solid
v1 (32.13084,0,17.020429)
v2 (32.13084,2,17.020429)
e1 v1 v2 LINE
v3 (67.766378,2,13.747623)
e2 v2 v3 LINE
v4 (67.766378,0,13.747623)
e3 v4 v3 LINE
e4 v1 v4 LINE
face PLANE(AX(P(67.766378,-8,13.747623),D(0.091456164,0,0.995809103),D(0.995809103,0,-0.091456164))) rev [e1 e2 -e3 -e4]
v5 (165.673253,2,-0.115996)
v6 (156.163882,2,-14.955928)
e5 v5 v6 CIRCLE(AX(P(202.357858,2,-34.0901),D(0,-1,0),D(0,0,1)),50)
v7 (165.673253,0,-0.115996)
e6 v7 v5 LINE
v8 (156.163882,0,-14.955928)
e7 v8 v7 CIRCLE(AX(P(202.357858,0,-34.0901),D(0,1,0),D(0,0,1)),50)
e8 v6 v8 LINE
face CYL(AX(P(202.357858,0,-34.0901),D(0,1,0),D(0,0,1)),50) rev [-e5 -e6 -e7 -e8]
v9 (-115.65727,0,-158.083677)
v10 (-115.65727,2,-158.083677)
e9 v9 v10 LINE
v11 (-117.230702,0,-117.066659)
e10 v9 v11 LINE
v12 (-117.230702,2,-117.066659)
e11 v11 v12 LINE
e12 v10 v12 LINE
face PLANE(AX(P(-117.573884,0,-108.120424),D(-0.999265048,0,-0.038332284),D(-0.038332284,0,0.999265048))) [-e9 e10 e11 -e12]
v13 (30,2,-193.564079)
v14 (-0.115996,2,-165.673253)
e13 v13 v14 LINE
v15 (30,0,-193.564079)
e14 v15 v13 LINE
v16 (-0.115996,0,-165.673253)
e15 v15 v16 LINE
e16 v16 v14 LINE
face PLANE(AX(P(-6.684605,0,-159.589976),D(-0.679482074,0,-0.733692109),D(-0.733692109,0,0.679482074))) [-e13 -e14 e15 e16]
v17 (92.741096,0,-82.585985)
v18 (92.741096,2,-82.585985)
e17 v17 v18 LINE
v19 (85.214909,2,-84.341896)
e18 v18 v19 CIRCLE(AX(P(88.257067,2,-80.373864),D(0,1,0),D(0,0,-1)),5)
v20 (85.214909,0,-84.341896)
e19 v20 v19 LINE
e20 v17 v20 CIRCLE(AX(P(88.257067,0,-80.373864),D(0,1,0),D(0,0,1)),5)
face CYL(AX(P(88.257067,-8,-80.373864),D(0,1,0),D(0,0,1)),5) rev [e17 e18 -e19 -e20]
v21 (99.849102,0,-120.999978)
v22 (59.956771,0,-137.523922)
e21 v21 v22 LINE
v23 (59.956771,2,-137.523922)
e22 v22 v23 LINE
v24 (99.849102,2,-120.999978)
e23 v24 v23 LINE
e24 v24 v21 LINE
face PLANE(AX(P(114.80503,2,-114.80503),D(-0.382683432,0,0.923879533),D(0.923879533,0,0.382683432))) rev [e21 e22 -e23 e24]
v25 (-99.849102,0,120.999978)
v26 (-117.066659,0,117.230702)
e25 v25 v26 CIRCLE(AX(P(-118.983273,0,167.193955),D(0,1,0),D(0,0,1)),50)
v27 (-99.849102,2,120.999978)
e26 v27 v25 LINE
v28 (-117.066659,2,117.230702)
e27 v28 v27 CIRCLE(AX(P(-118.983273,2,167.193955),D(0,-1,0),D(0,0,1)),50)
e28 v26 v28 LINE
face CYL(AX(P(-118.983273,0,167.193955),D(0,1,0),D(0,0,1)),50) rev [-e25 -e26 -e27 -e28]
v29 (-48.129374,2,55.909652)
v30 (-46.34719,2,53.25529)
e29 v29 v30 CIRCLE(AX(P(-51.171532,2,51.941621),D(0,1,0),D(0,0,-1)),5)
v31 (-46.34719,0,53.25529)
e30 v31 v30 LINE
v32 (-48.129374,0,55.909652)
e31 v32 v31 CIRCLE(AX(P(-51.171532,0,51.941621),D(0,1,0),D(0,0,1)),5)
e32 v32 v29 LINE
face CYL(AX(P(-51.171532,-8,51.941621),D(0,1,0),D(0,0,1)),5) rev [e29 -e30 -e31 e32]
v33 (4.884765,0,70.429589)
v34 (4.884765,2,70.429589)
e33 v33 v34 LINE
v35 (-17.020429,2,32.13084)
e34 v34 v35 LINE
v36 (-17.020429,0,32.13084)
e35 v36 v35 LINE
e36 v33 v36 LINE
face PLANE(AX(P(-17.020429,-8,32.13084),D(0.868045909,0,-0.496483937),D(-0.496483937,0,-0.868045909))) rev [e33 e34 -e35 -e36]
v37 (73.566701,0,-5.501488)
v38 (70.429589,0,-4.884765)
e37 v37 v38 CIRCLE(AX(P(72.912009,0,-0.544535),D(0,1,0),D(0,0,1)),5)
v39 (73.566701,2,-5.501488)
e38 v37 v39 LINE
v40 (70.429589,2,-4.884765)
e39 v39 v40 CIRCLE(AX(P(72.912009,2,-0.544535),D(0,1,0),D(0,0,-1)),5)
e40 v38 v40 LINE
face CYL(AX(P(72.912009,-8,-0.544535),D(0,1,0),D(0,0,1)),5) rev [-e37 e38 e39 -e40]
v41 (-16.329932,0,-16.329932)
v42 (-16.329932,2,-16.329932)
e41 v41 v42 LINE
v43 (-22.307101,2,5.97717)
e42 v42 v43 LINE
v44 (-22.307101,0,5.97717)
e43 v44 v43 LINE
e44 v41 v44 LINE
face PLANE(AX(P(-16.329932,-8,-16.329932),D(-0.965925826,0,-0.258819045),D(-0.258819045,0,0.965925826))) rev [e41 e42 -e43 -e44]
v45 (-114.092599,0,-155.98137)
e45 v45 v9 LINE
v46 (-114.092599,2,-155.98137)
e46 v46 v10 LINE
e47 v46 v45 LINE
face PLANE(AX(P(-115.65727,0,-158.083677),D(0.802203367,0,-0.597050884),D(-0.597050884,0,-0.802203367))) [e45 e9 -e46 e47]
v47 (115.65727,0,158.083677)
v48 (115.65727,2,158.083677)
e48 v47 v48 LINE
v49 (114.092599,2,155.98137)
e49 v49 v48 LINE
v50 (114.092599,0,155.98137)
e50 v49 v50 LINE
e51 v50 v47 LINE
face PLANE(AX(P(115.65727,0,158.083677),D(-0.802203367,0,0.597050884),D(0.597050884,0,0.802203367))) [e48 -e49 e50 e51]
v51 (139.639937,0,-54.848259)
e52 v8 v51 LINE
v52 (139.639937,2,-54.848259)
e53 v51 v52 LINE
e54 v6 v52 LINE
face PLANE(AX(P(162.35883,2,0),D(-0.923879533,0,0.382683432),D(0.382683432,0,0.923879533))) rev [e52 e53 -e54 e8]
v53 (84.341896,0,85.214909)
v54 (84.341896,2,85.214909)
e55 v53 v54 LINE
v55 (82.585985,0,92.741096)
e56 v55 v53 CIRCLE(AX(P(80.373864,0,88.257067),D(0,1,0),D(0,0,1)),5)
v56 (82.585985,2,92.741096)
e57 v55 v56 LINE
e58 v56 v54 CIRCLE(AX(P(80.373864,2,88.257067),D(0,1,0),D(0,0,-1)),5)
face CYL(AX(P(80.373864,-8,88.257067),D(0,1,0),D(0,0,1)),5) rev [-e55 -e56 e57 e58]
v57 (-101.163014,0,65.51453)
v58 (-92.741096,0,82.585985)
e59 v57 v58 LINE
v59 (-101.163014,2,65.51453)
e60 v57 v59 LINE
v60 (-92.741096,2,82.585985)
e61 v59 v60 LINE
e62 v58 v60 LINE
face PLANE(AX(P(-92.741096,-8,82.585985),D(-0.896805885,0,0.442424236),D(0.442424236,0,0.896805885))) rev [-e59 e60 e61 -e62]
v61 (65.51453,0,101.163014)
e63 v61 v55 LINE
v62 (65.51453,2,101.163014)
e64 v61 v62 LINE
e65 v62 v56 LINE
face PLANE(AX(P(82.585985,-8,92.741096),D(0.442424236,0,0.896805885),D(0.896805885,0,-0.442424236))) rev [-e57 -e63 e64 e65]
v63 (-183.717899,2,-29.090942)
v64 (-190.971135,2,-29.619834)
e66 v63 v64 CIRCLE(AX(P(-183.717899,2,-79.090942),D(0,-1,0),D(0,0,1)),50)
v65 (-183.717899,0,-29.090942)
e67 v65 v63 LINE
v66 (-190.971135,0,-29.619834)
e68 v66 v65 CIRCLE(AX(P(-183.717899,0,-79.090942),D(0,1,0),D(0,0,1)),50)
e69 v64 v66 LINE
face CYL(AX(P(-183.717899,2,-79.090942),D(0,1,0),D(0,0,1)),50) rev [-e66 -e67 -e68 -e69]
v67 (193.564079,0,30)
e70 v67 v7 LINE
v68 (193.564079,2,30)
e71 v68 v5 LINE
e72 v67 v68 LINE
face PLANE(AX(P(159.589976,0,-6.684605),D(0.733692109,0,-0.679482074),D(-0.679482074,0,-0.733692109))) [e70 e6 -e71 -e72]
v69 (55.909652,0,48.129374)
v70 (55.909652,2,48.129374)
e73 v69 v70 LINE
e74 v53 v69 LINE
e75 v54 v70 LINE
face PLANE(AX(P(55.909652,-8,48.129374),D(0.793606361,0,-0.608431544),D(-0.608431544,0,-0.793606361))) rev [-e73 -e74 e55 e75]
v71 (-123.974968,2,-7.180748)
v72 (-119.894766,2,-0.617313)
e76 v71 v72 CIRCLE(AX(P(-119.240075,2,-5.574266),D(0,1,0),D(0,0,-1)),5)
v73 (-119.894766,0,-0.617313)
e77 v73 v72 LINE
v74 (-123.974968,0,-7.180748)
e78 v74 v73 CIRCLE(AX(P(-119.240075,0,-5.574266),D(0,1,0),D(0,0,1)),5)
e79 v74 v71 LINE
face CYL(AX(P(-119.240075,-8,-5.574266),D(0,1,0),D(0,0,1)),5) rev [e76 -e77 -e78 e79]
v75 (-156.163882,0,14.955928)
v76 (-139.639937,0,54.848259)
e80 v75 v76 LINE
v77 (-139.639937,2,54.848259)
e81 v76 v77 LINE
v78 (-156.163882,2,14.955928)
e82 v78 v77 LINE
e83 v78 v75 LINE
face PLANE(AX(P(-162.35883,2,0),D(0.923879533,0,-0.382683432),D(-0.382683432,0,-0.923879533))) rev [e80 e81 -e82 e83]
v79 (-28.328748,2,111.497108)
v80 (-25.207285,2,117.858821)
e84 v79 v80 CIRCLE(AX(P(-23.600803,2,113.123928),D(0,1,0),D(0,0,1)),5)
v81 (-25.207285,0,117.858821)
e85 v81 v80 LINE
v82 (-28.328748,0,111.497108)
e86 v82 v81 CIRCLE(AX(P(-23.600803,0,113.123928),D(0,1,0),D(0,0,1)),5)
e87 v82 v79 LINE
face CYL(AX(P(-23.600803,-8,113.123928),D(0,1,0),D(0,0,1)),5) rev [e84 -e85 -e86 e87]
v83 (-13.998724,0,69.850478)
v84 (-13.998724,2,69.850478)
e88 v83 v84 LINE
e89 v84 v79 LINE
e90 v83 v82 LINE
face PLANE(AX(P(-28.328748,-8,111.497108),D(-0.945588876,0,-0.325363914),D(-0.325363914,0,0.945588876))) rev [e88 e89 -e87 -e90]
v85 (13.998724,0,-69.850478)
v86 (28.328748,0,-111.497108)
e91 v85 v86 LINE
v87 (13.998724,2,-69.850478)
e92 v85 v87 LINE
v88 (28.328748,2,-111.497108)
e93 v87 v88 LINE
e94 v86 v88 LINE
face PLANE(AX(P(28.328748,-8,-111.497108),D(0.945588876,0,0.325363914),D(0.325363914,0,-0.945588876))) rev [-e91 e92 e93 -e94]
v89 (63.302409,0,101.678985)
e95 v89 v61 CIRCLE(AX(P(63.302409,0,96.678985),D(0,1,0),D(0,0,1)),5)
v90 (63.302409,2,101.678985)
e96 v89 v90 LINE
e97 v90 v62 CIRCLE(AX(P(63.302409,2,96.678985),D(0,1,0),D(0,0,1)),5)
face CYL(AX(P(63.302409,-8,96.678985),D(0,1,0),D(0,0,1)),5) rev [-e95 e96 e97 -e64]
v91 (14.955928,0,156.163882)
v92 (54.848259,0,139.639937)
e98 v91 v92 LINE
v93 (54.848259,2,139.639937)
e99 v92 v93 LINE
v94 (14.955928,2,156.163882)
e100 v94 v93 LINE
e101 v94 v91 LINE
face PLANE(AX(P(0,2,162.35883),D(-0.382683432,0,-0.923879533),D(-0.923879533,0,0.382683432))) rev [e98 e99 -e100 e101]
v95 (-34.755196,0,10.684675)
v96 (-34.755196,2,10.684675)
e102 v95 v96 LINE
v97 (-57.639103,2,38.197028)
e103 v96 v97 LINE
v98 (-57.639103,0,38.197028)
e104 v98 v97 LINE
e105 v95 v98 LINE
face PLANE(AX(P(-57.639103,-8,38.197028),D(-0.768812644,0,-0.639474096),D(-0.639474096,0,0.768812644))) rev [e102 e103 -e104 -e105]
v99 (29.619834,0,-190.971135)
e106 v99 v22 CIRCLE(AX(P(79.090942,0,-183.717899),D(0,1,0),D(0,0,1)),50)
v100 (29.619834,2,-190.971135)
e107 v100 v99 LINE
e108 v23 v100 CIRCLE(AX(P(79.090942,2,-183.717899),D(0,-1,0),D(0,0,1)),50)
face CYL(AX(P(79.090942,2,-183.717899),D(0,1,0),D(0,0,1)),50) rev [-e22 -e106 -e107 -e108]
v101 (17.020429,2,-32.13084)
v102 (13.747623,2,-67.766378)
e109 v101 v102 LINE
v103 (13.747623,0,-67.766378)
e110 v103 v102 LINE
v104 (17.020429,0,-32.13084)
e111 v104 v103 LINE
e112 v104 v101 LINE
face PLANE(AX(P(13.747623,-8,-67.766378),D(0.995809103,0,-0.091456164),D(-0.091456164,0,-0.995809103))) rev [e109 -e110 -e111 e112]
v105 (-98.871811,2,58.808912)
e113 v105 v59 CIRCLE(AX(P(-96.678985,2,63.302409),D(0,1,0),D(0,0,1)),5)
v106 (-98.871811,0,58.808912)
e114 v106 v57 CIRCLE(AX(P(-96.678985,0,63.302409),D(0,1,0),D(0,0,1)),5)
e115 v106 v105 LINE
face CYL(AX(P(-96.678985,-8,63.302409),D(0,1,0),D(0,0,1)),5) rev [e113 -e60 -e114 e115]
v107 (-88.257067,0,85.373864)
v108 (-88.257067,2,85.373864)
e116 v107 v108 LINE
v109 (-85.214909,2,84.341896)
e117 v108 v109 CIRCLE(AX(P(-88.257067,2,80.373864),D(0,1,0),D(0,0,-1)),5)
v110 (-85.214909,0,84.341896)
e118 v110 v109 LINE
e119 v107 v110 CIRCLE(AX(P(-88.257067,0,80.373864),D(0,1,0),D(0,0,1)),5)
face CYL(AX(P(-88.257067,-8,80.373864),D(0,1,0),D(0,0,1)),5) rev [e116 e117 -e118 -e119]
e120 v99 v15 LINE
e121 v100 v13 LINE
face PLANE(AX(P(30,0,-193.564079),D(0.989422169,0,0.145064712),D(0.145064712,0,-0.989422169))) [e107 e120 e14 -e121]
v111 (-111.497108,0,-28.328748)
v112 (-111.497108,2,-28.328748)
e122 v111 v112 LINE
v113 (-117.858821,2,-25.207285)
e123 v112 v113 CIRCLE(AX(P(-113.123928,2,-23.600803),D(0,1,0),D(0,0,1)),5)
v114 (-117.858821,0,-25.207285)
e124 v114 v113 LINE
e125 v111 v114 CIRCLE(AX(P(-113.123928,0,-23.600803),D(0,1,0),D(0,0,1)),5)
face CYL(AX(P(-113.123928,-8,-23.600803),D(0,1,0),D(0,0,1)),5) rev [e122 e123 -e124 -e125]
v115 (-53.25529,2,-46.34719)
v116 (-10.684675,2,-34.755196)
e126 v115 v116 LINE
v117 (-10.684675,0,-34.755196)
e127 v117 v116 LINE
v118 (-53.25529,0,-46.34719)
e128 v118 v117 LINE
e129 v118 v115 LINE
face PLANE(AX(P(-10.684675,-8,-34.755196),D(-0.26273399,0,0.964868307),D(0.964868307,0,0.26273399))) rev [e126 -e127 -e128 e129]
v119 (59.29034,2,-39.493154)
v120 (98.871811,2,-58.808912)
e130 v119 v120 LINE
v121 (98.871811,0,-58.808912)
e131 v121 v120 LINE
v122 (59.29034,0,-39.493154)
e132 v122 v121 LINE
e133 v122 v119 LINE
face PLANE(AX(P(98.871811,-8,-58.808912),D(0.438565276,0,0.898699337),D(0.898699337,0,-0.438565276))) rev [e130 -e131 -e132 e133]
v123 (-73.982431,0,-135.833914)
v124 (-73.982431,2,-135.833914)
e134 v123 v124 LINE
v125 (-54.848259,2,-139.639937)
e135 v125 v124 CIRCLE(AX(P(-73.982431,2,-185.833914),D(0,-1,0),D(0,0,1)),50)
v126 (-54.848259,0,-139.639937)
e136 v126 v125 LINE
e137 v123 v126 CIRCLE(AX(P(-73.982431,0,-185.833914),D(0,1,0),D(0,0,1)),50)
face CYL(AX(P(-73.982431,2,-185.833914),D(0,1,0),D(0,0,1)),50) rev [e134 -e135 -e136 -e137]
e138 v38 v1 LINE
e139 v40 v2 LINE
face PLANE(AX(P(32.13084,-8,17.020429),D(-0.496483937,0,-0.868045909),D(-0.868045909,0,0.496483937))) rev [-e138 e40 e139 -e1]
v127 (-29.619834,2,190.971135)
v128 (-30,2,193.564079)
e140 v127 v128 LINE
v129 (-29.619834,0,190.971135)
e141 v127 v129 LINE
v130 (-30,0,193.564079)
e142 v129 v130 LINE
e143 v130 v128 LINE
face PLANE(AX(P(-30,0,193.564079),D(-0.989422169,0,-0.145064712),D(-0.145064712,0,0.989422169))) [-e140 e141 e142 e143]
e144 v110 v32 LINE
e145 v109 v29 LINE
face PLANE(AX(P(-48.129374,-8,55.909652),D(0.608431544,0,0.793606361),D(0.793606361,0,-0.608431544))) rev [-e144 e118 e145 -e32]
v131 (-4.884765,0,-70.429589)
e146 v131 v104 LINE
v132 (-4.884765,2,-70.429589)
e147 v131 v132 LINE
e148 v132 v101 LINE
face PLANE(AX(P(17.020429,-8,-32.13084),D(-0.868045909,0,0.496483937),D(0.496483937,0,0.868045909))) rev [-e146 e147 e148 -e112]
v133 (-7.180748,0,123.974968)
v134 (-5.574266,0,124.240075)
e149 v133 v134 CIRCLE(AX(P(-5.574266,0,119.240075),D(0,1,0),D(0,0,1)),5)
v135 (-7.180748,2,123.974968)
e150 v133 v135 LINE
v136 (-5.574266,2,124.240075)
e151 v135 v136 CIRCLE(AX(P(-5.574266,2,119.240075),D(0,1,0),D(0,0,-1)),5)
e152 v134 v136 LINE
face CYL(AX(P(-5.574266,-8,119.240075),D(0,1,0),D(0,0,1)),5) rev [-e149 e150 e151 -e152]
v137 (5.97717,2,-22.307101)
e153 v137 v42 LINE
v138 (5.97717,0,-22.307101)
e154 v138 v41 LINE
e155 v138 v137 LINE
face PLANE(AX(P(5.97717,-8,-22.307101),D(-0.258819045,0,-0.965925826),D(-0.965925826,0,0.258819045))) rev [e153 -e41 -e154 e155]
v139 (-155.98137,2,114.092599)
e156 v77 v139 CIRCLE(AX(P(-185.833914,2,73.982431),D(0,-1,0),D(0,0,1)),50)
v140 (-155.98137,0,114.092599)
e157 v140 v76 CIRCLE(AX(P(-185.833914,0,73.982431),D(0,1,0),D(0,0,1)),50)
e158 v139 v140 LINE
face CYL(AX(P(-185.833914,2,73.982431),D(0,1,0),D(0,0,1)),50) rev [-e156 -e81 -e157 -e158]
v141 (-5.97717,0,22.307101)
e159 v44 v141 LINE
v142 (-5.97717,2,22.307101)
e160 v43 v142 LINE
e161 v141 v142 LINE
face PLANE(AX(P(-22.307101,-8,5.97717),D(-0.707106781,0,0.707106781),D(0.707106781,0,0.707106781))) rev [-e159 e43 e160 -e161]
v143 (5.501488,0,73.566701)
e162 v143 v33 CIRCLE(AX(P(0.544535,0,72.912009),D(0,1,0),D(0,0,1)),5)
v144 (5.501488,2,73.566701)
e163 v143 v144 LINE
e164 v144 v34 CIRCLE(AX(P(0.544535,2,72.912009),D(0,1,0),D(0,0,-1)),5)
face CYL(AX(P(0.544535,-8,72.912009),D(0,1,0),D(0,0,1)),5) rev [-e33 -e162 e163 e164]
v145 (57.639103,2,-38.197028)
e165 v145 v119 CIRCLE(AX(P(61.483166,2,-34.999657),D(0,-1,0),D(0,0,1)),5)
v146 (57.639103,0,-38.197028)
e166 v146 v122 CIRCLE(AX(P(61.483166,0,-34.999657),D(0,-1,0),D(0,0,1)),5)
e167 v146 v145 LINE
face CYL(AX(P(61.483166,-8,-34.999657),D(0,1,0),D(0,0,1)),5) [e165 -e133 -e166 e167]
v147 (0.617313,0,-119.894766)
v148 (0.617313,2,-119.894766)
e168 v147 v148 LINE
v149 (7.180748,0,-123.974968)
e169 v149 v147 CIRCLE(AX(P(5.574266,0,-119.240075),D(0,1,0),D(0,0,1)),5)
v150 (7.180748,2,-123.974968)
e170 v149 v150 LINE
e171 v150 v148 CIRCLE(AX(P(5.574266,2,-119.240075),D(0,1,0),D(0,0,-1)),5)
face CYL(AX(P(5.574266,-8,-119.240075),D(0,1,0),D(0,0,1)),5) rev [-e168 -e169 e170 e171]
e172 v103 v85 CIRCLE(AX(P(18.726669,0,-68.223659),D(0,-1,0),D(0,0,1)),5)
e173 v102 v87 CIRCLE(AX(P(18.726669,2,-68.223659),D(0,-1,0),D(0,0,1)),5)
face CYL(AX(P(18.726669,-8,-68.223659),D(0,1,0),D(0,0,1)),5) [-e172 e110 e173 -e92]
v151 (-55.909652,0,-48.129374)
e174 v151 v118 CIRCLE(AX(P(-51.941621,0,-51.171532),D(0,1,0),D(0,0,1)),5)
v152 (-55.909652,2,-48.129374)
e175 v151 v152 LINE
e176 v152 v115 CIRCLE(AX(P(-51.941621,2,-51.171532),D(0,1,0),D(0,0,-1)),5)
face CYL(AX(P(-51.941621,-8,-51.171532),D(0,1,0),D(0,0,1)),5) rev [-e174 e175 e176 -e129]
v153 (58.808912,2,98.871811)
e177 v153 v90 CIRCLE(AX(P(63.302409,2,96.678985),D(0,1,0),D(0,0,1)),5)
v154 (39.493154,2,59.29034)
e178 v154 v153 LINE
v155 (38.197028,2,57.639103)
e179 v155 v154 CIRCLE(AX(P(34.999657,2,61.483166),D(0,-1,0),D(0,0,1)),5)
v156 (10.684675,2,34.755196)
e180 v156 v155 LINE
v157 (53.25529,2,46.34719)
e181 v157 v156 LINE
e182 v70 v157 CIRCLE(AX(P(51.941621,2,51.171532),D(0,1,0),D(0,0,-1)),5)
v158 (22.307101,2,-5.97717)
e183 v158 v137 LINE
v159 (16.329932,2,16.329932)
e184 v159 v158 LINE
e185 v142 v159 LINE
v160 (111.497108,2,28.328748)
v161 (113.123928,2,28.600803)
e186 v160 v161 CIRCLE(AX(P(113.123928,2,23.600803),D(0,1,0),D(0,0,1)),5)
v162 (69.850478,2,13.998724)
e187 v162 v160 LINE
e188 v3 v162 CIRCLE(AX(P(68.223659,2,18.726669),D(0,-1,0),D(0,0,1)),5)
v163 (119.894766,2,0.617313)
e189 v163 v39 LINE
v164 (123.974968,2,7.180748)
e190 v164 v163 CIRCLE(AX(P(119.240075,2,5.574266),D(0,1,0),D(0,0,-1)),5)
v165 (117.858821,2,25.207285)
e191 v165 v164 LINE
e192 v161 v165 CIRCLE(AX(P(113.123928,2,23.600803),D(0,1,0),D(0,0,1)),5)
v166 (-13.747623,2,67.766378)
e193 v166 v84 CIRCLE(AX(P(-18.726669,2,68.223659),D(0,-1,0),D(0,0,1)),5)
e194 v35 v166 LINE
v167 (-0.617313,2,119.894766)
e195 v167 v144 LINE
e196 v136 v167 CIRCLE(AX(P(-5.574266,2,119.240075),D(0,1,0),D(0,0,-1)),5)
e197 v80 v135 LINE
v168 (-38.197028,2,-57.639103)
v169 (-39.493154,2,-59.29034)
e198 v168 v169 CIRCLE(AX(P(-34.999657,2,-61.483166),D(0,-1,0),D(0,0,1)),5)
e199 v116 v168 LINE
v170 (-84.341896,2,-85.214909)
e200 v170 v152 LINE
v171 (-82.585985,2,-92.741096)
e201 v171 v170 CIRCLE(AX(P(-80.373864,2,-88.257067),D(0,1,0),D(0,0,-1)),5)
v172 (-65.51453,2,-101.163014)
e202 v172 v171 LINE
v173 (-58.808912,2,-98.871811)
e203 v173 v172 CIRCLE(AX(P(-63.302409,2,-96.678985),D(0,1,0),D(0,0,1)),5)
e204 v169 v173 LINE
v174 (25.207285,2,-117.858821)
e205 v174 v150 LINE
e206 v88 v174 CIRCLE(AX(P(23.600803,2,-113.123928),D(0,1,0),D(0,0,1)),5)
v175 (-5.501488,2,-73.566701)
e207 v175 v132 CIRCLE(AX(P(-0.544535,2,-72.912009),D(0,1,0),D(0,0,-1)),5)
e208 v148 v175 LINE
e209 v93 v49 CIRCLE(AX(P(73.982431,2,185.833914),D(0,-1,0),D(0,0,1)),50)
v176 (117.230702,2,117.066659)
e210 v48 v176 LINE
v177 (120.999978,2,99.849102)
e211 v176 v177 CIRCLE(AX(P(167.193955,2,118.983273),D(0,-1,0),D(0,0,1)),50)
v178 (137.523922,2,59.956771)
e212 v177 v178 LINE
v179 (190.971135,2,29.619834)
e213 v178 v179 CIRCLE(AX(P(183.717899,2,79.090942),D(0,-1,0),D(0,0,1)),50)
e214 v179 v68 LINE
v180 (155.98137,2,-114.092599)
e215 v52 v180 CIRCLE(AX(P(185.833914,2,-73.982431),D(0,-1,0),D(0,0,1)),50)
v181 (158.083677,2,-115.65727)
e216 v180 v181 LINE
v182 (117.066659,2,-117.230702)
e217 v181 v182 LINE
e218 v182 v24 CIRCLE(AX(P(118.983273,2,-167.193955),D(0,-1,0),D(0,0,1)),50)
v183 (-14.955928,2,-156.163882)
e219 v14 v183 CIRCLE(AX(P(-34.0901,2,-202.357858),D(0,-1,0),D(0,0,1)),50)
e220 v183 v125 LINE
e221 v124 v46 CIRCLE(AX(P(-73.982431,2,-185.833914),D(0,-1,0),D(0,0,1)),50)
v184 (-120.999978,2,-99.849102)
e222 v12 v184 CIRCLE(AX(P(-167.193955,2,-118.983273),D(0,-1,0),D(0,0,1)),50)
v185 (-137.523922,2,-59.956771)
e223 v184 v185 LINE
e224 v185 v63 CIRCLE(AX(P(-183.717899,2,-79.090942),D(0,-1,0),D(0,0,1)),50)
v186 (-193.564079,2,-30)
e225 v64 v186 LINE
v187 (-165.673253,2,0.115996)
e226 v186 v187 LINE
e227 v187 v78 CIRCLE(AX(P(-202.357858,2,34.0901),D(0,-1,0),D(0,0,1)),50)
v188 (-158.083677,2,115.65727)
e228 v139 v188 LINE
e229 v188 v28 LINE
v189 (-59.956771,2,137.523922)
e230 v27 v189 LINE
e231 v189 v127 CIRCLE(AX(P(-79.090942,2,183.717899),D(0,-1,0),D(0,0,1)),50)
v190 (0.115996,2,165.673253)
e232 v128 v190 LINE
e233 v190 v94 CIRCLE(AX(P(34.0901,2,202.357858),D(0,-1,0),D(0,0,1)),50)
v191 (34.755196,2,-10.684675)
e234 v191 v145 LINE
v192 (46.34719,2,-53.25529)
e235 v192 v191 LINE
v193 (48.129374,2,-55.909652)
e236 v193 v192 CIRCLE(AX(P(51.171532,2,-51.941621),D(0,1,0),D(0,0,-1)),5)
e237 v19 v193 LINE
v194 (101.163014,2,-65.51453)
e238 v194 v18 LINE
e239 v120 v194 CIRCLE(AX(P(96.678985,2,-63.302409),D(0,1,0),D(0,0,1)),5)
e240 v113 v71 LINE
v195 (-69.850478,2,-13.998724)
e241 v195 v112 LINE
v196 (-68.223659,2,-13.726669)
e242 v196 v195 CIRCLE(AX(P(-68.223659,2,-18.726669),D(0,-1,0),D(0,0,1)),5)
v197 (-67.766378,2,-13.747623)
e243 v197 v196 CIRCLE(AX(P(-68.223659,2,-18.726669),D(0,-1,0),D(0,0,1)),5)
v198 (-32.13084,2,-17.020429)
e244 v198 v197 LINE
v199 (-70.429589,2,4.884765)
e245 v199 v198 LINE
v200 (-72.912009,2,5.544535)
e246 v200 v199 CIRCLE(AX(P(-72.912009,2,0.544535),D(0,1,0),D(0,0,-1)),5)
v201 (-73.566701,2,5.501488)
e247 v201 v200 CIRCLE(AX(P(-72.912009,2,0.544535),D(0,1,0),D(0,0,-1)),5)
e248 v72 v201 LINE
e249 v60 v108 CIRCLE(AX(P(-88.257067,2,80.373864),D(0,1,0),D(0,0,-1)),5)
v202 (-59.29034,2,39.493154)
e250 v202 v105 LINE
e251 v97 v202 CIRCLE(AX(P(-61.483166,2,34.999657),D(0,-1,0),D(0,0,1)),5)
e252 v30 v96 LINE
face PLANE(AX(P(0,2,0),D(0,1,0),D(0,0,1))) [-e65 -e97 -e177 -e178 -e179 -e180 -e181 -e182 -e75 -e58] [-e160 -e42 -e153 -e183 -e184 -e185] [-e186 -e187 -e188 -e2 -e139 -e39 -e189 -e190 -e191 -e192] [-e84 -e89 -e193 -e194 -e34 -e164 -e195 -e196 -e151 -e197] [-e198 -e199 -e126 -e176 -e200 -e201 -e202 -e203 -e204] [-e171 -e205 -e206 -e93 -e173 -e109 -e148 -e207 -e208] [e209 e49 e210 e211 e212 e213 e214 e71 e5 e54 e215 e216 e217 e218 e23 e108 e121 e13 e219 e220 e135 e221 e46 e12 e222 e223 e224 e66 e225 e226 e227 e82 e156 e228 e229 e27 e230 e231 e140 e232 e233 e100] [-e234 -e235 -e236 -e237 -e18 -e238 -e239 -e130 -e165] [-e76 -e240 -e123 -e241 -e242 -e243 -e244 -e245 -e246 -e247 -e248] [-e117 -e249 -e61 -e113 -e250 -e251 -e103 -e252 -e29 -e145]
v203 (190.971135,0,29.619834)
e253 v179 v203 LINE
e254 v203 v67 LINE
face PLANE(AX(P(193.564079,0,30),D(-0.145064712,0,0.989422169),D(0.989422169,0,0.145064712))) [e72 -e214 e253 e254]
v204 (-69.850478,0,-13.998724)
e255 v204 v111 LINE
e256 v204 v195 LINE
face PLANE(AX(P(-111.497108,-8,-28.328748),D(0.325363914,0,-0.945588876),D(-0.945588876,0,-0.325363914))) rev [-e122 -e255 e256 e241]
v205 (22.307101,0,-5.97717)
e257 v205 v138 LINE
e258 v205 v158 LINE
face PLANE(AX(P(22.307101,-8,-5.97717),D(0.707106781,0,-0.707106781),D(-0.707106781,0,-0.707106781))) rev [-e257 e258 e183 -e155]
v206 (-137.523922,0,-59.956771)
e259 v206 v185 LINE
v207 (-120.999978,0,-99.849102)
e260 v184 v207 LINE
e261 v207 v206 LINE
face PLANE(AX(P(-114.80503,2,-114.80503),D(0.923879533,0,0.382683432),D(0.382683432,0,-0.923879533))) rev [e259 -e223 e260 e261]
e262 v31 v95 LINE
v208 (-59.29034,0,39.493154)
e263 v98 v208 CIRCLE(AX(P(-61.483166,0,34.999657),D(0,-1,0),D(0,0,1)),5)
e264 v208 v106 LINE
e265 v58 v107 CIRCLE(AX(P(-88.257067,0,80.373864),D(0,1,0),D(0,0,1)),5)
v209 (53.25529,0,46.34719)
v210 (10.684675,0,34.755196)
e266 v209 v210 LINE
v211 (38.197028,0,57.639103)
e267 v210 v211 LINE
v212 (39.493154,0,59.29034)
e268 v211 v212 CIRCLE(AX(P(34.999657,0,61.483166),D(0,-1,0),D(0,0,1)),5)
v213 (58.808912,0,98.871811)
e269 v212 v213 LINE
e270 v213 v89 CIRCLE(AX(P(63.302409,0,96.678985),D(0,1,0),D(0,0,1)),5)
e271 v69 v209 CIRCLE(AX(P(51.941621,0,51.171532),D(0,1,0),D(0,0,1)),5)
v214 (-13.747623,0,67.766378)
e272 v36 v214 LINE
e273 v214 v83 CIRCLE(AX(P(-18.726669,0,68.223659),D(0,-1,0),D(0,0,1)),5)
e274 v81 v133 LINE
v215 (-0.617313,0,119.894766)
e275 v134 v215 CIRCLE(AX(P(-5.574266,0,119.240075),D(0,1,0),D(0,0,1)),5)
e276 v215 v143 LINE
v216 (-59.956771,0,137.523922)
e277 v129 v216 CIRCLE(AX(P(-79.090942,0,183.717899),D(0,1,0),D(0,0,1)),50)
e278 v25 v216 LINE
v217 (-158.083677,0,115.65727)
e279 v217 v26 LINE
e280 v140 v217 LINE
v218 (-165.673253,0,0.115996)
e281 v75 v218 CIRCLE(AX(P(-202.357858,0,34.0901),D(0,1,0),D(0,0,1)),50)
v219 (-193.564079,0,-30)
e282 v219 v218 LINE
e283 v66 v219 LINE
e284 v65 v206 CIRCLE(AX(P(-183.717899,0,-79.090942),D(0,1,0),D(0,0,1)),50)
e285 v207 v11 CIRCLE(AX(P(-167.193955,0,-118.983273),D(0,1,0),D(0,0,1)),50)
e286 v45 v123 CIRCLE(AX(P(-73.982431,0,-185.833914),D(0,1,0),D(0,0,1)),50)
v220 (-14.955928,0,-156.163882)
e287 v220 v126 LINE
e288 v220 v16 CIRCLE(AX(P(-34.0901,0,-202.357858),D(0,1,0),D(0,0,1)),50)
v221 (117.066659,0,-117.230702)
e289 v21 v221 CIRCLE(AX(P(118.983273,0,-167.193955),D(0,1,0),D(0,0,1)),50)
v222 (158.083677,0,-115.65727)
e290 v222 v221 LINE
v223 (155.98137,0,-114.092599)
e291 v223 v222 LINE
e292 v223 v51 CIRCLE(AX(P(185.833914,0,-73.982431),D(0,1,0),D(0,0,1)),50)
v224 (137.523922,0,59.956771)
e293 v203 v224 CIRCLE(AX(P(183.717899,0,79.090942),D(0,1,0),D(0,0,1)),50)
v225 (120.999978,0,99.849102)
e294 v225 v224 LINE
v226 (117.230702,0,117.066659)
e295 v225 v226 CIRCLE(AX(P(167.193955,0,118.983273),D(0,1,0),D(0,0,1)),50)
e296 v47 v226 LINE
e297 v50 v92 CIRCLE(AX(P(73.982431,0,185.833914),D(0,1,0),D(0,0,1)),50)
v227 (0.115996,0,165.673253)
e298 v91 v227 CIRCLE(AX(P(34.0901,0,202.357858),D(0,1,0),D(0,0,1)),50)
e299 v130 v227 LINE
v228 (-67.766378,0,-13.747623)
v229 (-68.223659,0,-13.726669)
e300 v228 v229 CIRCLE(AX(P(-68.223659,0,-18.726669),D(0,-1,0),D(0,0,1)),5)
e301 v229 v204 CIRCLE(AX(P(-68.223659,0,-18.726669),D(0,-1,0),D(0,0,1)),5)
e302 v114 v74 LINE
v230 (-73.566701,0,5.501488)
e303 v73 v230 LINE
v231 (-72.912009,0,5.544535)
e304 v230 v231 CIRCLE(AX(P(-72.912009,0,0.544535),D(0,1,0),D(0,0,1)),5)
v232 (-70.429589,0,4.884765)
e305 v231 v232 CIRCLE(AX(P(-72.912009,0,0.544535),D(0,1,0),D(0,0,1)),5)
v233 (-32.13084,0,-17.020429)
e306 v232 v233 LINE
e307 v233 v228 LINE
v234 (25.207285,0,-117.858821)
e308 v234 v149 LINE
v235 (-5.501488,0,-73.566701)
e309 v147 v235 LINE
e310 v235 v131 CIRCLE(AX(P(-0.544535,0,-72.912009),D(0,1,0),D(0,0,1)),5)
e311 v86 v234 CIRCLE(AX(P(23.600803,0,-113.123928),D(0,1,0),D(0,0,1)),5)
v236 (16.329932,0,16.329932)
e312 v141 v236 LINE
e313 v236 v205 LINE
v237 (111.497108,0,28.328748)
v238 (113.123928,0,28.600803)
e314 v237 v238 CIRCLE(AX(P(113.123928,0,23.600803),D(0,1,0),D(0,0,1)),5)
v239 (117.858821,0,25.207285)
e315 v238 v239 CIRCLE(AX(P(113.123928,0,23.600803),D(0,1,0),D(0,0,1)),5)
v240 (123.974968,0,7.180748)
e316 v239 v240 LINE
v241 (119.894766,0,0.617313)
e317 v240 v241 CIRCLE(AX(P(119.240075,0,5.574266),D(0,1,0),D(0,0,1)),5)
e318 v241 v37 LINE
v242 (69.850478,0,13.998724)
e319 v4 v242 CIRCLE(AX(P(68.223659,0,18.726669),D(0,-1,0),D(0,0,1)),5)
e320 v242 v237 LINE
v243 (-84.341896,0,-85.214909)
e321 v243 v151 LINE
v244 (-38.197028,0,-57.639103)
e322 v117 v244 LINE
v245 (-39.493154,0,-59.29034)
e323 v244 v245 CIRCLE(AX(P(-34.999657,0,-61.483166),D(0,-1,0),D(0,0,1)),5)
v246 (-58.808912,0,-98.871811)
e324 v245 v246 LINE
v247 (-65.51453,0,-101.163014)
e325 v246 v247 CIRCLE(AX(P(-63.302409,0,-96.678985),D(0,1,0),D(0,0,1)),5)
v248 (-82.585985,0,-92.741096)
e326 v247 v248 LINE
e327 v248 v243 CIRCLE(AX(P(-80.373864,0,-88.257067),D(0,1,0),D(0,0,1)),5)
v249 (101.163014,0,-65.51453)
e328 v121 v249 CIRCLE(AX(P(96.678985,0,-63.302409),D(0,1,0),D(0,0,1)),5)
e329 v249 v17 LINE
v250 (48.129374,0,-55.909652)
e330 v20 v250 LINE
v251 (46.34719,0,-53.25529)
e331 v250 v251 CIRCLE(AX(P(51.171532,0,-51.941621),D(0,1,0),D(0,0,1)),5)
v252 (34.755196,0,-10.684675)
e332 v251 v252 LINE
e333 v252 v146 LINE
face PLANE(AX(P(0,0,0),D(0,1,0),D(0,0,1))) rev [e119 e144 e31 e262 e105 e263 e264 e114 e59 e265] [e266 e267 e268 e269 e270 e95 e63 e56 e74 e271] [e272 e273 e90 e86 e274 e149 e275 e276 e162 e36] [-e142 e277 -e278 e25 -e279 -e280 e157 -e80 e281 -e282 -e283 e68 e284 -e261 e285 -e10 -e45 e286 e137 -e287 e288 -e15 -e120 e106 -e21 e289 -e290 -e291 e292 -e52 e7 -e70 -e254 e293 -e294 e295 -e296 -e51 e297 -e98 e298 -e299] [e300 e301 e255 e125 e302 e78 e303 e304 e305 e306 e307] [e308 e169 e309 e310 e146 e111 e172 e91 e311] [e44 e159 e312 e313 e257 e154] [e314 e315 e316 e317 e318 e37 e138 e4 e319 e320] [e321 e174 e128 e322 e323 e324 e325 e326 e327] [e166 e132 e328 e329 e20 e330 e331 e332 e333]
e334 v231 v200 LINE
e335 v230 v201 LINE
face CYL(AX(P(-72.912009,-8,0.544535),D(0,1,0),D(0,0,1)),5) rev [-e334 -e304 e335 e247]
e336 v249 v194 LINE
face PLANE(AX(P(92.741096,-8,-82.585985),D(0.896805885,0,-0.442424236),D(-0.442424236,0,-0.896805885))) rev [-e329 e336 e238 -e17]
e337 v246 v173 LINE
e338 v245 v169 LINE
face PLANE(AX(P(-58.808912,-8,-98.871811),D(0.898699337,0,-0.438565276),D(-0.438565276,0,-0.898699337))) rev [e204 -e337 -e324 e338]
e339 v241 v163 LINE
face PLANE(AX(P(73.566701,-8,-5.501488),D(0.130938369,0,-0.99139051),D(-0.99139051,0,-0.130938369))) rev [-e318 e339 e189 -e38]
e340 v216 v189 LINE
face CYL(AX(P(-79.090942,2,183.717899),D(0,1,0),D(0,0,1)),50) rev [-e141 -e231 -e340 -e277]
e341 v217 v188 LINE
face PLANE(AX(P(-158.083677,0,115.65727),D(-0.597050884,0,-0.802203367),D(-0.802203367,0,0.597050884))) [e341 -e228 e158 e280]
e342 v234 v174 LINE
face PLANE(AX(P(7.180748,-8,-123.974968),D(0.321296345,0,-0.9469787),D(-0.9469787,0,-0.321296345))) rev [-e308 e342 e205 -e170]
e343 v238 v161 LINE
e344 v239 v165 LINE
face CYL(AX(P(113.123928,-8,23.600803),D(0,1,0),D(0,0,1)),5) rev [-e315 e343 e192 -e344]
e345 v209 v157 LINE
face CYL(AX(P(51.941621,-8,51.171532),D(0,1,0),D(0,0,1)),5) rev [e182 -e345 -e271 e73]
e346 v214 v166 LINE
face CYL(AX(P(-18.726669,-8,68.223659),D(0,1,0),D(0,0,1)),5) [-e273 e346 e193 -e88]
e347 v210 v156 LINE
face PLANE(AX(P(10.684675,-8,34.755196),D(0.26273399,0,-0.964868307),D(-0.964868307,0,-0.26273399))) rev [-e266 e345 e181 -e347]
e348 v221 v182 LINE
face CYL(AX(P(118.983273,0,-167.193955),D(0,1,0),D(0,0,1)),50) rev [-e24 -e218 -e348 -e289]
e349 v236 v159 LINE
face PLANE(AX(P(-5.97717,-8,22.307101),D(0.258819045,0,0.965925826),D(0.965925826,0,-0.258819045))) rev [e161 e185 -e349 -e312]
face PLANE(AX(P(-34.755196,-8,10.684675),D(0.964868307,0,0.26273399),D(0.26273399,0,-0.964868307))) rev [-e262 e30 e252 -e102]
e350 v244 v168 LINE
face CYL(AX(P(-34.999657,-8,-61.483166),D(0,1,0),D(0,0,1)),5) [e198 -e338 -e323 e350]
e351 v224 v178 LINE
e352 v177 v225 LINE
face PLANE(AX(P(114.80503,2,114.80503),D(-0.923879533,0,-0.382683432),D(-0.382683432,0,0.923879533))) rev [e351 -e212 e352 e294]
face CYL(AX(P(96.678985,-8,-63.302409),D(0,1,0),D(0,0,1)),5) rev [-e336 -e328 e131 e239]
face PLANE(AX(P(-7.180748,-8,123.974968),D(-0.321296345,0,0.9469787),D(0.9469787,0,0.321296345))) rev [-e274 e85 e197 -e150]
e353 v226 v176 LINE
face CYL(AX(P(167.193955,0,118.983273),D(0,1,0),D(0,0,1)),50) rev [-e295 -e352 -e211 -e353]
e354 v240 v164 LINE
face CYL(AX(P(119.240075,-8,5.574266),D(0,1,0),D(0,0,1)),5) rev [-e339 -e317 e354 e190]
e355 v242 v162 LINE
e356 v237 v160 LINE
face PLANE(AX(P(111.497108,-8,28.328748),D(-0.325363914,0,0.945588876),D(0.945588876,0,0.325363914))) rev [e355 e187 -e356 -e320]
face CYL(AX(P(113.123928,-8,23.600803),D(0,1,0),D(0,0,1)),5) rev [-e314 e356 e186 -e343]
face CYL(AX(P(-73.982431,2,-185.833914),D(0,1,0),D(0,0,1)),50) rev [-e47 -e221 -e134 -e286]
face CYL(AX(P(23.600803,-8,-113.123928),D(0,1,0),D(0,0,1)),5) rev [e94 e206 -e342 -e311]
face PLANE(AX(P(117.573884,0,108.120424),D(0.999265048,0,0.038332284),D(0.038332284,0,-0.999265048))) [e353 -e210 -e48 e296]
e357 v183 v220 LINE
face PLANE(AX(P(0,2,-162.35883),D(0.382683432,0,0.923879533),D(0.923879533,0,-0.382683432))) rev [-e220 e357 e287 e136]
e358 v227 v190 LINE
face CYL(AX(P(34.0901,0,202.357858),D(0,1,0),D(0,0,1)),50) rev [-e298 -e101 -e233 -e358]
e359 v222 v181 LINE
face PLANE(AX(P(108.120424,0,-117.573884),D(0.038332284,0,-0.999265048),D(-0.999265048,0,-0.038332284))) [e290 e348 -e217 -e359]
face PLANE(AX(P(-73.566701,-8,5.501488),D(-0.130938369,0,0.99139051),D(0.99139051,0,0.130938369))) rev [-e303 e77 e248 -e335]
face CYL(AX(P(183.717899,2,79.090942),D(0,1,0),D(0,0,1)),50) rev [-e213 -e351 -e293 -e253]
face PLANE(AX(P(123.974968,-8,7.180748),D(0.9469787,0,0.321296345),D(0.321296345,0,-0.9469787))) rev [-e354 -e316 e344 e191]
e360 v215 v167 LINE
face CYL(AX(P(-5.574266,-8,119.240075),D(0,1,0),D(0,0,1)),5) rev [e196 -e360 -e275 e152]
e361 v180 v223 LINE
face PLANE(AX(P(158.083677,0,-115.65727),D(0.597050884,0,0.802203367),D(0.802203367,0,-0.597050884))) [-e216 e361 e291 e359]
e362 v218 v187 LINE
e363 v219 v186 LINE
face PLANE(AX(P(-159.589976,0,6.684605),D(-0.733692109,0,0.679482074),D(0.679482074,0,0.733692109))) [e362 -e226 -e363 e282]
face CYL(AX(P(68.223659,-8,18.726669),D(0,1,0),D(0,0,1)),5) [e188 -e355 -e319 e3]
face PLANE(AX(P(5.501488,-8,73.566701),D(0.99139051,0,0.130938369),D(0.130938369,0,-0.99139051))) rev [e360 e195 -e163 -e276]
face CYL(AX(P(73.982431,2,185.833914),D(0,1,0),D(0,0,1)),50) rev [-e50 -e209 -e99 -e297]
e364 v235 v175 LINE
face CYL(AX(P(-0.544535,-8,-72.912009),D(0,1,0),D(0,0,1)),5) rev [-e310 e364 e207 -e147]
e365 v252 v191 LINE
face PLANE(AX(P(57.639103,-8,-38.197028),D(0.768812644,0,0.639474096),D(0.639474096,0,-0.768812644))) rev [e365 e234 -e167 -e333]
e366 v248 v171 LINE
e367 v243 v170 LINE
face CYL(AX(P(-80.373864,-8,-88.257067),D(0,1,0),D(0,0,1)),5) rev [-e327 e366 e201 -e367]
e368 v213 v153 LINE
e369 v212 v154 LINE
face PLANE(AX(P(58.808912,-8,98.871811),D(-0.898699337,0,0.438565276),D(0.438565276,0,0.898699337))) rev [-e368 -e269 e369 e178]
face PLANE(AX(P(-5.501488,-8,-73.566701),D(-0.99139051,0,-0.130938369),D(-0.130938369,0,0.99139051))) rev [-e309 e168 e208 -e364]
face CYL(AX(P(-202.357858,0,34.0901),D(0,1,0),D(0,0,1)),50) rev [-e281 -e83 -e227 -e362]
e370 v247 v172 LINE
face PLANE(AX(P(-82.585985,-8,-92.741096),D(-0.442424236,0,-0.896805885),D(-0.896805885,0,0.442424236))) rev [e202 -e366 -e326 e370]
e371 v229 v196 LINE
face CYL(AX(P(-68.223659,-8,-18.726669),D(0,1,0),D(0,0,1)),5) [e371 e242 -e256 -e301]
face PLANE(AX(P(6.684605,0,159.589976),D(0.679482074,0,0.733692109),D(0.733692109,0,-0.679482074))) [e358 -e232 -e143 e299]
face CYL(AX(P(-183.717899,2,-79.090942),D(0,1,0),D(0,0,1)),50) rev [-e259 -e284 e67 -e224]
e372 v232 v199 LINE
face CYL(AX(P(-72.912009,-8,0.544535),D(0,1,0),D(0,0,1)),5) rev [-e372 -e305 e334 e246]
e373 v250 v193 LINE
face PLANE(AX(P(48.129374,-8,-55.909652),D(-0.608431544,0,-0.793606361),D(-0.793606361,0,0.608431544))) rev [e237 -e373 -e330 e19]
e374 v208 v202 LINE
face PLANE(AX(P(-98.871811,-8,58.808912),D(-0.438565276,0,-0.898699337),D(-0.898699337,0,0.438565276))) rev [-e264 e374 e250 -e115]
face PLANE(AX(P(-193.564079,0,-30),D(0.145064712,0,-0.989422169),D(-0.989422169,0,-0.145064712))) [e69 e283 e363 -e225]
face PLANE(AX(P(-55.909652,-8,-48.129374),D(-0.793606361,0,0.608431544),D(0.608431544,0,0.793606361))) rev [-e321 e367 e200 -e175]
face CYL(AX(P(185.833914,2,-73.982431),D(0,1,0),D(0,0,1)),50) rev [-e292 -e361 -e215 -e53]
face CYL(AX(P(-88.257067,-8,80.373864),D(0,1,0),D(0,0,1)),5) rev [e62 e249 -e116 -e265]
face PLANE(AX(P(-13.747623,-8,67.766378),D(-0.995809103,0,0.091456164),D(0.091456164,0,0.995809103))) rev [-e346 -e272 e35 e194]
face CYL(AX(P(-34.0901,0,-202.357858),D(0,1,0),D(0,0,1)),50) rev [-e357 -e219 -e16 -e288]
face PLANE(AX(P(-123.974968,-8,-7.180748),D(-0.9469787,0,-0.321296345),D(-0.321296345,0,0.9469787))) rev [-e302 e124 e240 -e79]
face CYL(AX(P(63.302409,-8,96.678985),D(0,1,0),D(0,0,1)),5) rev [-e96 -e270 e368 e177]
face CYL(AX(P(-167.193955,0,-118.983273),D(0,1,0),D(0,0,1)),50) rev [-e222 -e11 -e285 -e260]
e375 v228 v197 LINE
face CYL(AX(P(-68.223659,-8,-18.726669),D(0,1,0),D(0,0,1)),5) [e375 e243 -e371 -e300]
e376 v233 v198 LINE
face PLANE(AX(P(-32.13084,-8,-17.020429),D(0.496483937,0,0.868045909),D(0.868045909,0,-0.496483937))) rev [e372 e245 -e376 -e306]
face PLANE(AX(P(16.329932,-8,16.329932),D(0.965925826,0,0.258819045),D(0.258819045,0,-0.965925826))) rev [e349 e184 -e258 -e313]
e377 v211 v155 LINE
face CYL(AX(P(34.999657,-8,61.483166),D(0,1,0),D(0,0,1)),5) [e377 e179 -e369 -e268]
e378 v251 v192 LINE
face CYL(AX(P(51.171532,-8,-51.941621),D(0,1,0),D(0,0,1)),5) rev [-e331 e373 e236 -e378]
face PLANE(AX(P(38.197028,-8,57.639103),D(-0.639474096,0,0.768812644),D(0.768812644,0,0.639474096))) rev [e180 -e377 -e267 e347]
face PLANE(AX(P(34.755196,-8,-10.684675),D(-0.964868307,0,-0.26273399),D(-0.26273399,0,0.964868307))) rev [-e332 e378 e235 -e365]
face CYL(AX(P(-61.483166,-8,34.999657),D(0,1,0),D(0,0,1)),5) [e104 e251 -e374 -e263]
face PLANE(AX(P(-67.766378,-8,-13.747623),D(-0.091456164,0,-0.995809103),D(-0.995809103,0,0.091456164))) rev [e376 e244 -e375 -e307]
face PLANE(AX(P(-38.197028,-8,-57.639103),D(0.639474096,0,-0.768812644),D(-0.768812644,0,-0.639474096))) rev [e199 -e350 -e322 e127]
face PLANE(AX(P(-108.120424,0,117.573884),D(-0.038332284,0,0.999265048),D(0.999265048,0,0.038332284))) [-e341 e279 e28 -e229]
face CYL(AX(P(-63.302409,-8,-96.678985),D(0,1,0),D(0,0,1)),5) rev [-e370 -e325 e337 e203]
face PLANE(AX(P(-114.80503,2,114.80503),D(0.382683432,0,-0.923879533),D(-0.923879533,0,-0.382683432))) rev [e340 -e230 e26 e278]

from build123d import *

# Parameters (mm, degrees)
BOSS_EXTRUDE1_DEPTH = 2
CUT_EXTRUDE1_DEPTH  = 10
CUT_EXTRUDE2_DEPTH  = 10
BOSS_EXTRUDE2_DEPTH = 2
FILLET1_R           = 50


with BuildPart() as part:
    # Sketch1 → Boss-Extrude1 (new body)
    with BuildSketch(Plane(origin=(0, 0, 0), x_dir=(1, 0, 0), z_dir=(0, 1, 0))):
        Polygon((114.80502971, -114.80502971), (162.358830044, 0), (114.80502971, 114.80502971), (0, 162.358830044), (-114.80502971, 114.80502971), (-162.358830044, 0), (-114.80502971, -114.80502971), (0, -162.358830044), align=None)
    extrude(amount=BOSS_EXTRUDE1_DEPTH)

    # Sketch2 → Cut-Extrude1 (cut)
    with BuildSketch(Plane(origin=(0, 2, 0), x_dir=(1, 0, 0), z_dir=(0, 1, 0))):
        Polygon((5.977169814, 22.307101433), (-16.329931619, 16.329931619), (-22.307101433, -5.977169814), (-5.977169814, -22.307101433), (16.329931619, -16.329931619), (22.307101433, 5.977169814), align=None)
    extrude(amount=-CUT_EXTRUDE1_DEPTH, mode=Mode.SUBTRACT)

    # Sketch3 → Cut-Extrude2 (cut)
    with BuildSketch(Plane(origin=(0, 2, 0), x_dir=(1, 0, 0), z_dir=(0, 1, 0))):
        with BuildLine():
            Line((7.180747689, 123.974968015), (25.207285, 117.858821427))
            ThreePointArc((25.207285, 117.858821427), (28.089576698, 115.326406795), (28.328747659, 111.497108353))
            Line((28.328747659, 111.497108353), (13.99872444, 69.850478373))
            ThreePointArc((13.99872444, 69.850478373), (13.762569524, 68.82175425), (13.747623306, 67.766377979))
            Line((13.747623306, 67.766377979), (17.02042887, 32.130840461))
            Line((17.02042887, 32.130840461), (-4.884764675, 70.429589412))
            ThreePointArc((-4.884764675, 70.429589412), (-5.450629901, 71.947522663), (-5.501487679, 73.566700941))
            Line((-5.501487679, 73.566700941), (0.617313414, 119.89476636))
            ThreePointArc((0.617313414, 119.89476636), (2.934488498, 123.486434711), (7.180747689, 123.974968015))
        make_face()
        with BuildLine():
            Line((92.741095966, 82.585985196), (101.163014013, 65.514529695))
            ThreePointArc((101.163014013, 65.514529695), (101.410414459, 61.68575413), (98.871810971, 58.808911827))
            Line((98.871810971, 58.808911827), (59.290339906, 39.493153947))
            ThreePointArc((59.290339906, 39.493153947), (58.395935361, 38.932722886), (57.63910307, 38.197027741))
            Line((57.63910307, 38.197027741), (34.755195848, 10.684674503))
            Line((34.755195848, 10.684674503), (46.347190043, 53.255290495))
            ThreePointArc((46.347190043, 53.255290495), (47.0204038, 54.72875853), (48.129373861, 55.909652349))
            Line((48.129373861, 55.909652349), (85.214908823, 84.34189582))
            ThreePointArc((85.214908823, 84.34189582), (89.393092084, 85.243098653), (92.741095966, 82.585985196))
        make_face()
        with BuildLine():
            Line((123.974968015, -7.180747689), (117.858821427, -25.207285))
            ThreePointArc((117.858821427, -25.207285), (115.326406795, -28.089576698), (111.497108353, -28.328747659))
            Line((111.497108353, -28.328747659), (69.850478373, -13.99872444))
            ThreePointArc((69.850478373, -13.99872444), (68.82175425, -13.762569524), (67.766377979, -13.747623306))
            Line((67.766377979, -13.747623306), (32.130840461, -17.02042887))
            Line((32.130840461, -17.02042887), (70.429589412, 4.884764675))
            ThreePointArc((70.429589412, 4.884764675), (71.947522663, 5.450629901), (73.566700941, 5.501487679))
            Line((73.566700941, 5.501487679), (119.89476636, -0.617313414))
            ThreePointArc((119.89476636, -0.617313414), (123.486434711, -2.934488498), (123.974968015, -7.180747689))
        make_face()
        with BuildLine():
            Line((82.585985196, -92.741095966), (65.514529695, -101.163014013))
            ThreePointArc((65.514529695, -101.163014013), (61.68575413, -101.410414459), (58.808911827, -98.871810971))
            Line((58.808911827, -98.871810971), (39.493153947, -59.290339906))
            ThreePointArc((39.493153947, -59.290339906), (38.932722886, -58.395935361), (38.197027741, -57.63910307))
            Line((38.197027741, -57.63910307), (10.684674503, -34.755195848))
            Line((10.684674503, -34.755195848), (53.255290495, -46.347190043))
            ThreePointArc((53.255290495, -46.347190043), (54.72875853, -47.0204038), (55.909652349, -48.129373861))
            Line((55.909652349, -48.129373861), (84.34189582, -85.214908823))
            ThreePointArc((84.34189582, -85.214908823), (85.243098653, -89.393092084), (82.585985196, -92.741095966))
        make_face()
        with BuildLine():
            Line((-7.180747689, -123.974968015), (-25.207285, -117.858821427))
            ThreePointArc((-25.207285, -117.858821427), (-28.089576698, -115.326406795), (-28.328747659, -111.497108353))
            Line((-28.328747659, -111.497108353), (-13.99872444, -69.850478373))
            ThreePointArc((-13.99872444, -69.850478373), (-13.762569524, -68.82175425), (-13.747623306, -67.766377979))
            Line((-13.747623306, -67.766377979), (-17.02042887, -32.130840461))
            Line((-17.02042887, -32.130840461), (4.884764675, -70.429589412))
            ThreePointArc((4.884764675, -70.429589412), (5.450629901, -71.947522663), (5.501487679, -73.566700941))
            Line((5.501487679, -73.566700941), (-0.617313414, -119.89476636))
            ThreePointArc((-0.617313414, -119.89476636), (-2.934488497, -123.486434711), (-7.180747689, -123.974968015))
        make_face()
        with BuildLine():
            Line((-92.741095966, -82.585985196), (-101.163014013, -65.514529695))
            ThreePointArc((-101.163014013, -65.514529695), (-101.410414459, -61.68575413), (-98.871810971, -58.808911827))
            Line((-98.871810971, -58.808911827), (-59.290339906, -39.493153947))
            ThreePointArc((-59.290339906, -39.493153947), (-58.395935361, -38.932722886), (-57.63910307, -38.197027741))
            Line((-57.63910307, -38.197027741), (-34.755195848, -10.684674503))
            Line((-34.755195848, -10.684674503), (-46.347190043, -53.255290495))
            ThreePointArc((-46.347190043, -53.255290495), (-47.0204038, -54.72875853), (-48.129373861, -55.909652349))
            Line((-48.129373861, -55.909652349), (-85.214908823, -84.34189582))
            ThreePointArc((-85.214908823, -84.34189582), (-89.393092084, -85.243098653), (-92.741095966, -82.585985196))
        make_face()
        with BuildLine():
            Line((-123.974968015, 7.180747689), (-117.858821427, 25.207285))
            ThreePointArc((-117.858821427, 25.207285), (-115.326406795, 28.089576698), (-111.497108353, 28.328747659))
            Line((-111.497108353, 28.328747659), (-69.850478373, 13.99872444))
            ThreePointArc((-69.850478373, 13.99872444), (-68.82175425, 13.762569524), (-67.766377979, 13.747623306))
            Line((-67.766377979, 13.747623306), (-32.130840461, 17.02042887))
            Line((-32.130840461, 17.02042887), (-70.429589412, -4.884764675))
            ThreePointArc((-70.429589412, -4.884764675), (-71.947522663, -5.450629901), (-73.566700941, -5.501487679))
            Line((-73.566700941, -5.501487679), (-119.89476636, 0.617313414))
            ThreePointArc((-119.89476636, 0.617313414), (-123.486434711, 2.934488497), (-123.974968015, 7.180747689))
        make_face()
        with BuildLine():
            Line((-82.585985196, 92.741095966), (-65.514529695, 101.163014013))
            ThreePointArc((-65.514529695, 101.163014013), (-61.68575413, 101.410414459), (-58.808911827, 98.871810971))
            Line((-58.808911827, 98.871810971), (-39.493153947, 59.290339906))
            ThreePointArc((-39.493153947, 59.290339906), (-38.932722886, 58.395935361), (-38.197027741, 57.63910307))
            Line((-38.197027741, 57.63910307), (-10.684674503, 34.755195848))
            Line((-10.684674503, 34.755195848), (-53.255290495, 46.347190043))
            ThreePointArc((-53.255290495, 46.347190043), (-54.72875853, 47.0204038), (-55.909652349, 48.129373861))
            Line((-55.909652349, 48.129373861), (-84.34189582, 85.214908823))
            ThreePointArc((-84.34189582, 85.214908823), (-85.243098653, 89.393092084), (-82.585985196, 92.741095966))
        make_face()
    extrude(amount=-CUT_EXTRUDE2_DEPTH, mode=Mode.SUBTRACT)

    # Sketch6 → Boss-Extrude2 (add)
    with BuildSketch(Plane(origin=(0, 2, 0), x_dir=(1, 0, 0), z_dir=(0, 1, 0))):
        Polygon((-117.573883954, 108.120424241), (-115.657269767, 158.083676638), (-90.835857439, 124.733385943), (-114.80502971, 114.80502971), align=None)
        Polygon((-6.684605468, 159.5899758), (30, 193.564079491), (23.969172271, 152.43047381), (0, 162.358830044), align=None)
        Polygon((108.120424241, 117.573883954), (158.083676638, 115.657269767), (124.733385943, 90.835857439), (114.80502971, 114.80502971), align=None)
        Polygon((159.5899758, 6.684605468), (193.564079491, -30), (152.43047381, -23.969172271), (162.358830044, 0), align=None)
        Polygon((117.573883954, -108.120424241), (115.657269767, -158.083676638), (90.835857439, -124.733385943), (114.80502971, -114.80502971), align=None)
        Polygon((6.684605468, -159.5899758), (-30, -193.564079491), (-23.969172271, -152.43047381), (0, -162.358830044), align=None)
        Polygon((-108.120424241, -117.573883954), (-158.083676638, -115.657269767), (-124.733385943, -90.835857439), (-114.80502971, -114.80502971), align=None)
        Polygon((-159.5899758, -6.684605468), (-193.564079491, 30), (-152.43047381, 23.969172271), (-162.358830044, 0), align=None)
    extrude(amount=-BOSS_EXTRUDE2_DEPTH)

    # Fillet1
    fillet1_edges = [part.edges().sort_by_distance(p)[0] for p in [
        (-117.573883954, 1, -108.120424241),
        (-90.835857439, 1, -124.733385943),
        (-6.684605468, 1, -159.5899758),
        (23.969172271, 1, -152.43047381),
        (108.120424241, 1, -117.573883954),
        (124.733385943, 1, -90.835857439),
        (159.5899758, 1, -6.684605468),
        (152.43047381, 1, 23.969172271),
        (117.573883954, 1, 108.120424241),
        (90.835857439, 1, 124.733385943),
        (6.684605468, 1, 159.5899758),
        (-23.969172271, 1, 152.43047381),
        (-108.120424241, 1, 117.573883954),
        (-124.733385943, 1, 90.835857439),
        (-159.5899758, 1, 6.684605468),
        (-152.43047381, 1, -23.969172271),
    ]]
    fillet(fillet1_edges, radius=FILLET1_R)


solid = part.part
